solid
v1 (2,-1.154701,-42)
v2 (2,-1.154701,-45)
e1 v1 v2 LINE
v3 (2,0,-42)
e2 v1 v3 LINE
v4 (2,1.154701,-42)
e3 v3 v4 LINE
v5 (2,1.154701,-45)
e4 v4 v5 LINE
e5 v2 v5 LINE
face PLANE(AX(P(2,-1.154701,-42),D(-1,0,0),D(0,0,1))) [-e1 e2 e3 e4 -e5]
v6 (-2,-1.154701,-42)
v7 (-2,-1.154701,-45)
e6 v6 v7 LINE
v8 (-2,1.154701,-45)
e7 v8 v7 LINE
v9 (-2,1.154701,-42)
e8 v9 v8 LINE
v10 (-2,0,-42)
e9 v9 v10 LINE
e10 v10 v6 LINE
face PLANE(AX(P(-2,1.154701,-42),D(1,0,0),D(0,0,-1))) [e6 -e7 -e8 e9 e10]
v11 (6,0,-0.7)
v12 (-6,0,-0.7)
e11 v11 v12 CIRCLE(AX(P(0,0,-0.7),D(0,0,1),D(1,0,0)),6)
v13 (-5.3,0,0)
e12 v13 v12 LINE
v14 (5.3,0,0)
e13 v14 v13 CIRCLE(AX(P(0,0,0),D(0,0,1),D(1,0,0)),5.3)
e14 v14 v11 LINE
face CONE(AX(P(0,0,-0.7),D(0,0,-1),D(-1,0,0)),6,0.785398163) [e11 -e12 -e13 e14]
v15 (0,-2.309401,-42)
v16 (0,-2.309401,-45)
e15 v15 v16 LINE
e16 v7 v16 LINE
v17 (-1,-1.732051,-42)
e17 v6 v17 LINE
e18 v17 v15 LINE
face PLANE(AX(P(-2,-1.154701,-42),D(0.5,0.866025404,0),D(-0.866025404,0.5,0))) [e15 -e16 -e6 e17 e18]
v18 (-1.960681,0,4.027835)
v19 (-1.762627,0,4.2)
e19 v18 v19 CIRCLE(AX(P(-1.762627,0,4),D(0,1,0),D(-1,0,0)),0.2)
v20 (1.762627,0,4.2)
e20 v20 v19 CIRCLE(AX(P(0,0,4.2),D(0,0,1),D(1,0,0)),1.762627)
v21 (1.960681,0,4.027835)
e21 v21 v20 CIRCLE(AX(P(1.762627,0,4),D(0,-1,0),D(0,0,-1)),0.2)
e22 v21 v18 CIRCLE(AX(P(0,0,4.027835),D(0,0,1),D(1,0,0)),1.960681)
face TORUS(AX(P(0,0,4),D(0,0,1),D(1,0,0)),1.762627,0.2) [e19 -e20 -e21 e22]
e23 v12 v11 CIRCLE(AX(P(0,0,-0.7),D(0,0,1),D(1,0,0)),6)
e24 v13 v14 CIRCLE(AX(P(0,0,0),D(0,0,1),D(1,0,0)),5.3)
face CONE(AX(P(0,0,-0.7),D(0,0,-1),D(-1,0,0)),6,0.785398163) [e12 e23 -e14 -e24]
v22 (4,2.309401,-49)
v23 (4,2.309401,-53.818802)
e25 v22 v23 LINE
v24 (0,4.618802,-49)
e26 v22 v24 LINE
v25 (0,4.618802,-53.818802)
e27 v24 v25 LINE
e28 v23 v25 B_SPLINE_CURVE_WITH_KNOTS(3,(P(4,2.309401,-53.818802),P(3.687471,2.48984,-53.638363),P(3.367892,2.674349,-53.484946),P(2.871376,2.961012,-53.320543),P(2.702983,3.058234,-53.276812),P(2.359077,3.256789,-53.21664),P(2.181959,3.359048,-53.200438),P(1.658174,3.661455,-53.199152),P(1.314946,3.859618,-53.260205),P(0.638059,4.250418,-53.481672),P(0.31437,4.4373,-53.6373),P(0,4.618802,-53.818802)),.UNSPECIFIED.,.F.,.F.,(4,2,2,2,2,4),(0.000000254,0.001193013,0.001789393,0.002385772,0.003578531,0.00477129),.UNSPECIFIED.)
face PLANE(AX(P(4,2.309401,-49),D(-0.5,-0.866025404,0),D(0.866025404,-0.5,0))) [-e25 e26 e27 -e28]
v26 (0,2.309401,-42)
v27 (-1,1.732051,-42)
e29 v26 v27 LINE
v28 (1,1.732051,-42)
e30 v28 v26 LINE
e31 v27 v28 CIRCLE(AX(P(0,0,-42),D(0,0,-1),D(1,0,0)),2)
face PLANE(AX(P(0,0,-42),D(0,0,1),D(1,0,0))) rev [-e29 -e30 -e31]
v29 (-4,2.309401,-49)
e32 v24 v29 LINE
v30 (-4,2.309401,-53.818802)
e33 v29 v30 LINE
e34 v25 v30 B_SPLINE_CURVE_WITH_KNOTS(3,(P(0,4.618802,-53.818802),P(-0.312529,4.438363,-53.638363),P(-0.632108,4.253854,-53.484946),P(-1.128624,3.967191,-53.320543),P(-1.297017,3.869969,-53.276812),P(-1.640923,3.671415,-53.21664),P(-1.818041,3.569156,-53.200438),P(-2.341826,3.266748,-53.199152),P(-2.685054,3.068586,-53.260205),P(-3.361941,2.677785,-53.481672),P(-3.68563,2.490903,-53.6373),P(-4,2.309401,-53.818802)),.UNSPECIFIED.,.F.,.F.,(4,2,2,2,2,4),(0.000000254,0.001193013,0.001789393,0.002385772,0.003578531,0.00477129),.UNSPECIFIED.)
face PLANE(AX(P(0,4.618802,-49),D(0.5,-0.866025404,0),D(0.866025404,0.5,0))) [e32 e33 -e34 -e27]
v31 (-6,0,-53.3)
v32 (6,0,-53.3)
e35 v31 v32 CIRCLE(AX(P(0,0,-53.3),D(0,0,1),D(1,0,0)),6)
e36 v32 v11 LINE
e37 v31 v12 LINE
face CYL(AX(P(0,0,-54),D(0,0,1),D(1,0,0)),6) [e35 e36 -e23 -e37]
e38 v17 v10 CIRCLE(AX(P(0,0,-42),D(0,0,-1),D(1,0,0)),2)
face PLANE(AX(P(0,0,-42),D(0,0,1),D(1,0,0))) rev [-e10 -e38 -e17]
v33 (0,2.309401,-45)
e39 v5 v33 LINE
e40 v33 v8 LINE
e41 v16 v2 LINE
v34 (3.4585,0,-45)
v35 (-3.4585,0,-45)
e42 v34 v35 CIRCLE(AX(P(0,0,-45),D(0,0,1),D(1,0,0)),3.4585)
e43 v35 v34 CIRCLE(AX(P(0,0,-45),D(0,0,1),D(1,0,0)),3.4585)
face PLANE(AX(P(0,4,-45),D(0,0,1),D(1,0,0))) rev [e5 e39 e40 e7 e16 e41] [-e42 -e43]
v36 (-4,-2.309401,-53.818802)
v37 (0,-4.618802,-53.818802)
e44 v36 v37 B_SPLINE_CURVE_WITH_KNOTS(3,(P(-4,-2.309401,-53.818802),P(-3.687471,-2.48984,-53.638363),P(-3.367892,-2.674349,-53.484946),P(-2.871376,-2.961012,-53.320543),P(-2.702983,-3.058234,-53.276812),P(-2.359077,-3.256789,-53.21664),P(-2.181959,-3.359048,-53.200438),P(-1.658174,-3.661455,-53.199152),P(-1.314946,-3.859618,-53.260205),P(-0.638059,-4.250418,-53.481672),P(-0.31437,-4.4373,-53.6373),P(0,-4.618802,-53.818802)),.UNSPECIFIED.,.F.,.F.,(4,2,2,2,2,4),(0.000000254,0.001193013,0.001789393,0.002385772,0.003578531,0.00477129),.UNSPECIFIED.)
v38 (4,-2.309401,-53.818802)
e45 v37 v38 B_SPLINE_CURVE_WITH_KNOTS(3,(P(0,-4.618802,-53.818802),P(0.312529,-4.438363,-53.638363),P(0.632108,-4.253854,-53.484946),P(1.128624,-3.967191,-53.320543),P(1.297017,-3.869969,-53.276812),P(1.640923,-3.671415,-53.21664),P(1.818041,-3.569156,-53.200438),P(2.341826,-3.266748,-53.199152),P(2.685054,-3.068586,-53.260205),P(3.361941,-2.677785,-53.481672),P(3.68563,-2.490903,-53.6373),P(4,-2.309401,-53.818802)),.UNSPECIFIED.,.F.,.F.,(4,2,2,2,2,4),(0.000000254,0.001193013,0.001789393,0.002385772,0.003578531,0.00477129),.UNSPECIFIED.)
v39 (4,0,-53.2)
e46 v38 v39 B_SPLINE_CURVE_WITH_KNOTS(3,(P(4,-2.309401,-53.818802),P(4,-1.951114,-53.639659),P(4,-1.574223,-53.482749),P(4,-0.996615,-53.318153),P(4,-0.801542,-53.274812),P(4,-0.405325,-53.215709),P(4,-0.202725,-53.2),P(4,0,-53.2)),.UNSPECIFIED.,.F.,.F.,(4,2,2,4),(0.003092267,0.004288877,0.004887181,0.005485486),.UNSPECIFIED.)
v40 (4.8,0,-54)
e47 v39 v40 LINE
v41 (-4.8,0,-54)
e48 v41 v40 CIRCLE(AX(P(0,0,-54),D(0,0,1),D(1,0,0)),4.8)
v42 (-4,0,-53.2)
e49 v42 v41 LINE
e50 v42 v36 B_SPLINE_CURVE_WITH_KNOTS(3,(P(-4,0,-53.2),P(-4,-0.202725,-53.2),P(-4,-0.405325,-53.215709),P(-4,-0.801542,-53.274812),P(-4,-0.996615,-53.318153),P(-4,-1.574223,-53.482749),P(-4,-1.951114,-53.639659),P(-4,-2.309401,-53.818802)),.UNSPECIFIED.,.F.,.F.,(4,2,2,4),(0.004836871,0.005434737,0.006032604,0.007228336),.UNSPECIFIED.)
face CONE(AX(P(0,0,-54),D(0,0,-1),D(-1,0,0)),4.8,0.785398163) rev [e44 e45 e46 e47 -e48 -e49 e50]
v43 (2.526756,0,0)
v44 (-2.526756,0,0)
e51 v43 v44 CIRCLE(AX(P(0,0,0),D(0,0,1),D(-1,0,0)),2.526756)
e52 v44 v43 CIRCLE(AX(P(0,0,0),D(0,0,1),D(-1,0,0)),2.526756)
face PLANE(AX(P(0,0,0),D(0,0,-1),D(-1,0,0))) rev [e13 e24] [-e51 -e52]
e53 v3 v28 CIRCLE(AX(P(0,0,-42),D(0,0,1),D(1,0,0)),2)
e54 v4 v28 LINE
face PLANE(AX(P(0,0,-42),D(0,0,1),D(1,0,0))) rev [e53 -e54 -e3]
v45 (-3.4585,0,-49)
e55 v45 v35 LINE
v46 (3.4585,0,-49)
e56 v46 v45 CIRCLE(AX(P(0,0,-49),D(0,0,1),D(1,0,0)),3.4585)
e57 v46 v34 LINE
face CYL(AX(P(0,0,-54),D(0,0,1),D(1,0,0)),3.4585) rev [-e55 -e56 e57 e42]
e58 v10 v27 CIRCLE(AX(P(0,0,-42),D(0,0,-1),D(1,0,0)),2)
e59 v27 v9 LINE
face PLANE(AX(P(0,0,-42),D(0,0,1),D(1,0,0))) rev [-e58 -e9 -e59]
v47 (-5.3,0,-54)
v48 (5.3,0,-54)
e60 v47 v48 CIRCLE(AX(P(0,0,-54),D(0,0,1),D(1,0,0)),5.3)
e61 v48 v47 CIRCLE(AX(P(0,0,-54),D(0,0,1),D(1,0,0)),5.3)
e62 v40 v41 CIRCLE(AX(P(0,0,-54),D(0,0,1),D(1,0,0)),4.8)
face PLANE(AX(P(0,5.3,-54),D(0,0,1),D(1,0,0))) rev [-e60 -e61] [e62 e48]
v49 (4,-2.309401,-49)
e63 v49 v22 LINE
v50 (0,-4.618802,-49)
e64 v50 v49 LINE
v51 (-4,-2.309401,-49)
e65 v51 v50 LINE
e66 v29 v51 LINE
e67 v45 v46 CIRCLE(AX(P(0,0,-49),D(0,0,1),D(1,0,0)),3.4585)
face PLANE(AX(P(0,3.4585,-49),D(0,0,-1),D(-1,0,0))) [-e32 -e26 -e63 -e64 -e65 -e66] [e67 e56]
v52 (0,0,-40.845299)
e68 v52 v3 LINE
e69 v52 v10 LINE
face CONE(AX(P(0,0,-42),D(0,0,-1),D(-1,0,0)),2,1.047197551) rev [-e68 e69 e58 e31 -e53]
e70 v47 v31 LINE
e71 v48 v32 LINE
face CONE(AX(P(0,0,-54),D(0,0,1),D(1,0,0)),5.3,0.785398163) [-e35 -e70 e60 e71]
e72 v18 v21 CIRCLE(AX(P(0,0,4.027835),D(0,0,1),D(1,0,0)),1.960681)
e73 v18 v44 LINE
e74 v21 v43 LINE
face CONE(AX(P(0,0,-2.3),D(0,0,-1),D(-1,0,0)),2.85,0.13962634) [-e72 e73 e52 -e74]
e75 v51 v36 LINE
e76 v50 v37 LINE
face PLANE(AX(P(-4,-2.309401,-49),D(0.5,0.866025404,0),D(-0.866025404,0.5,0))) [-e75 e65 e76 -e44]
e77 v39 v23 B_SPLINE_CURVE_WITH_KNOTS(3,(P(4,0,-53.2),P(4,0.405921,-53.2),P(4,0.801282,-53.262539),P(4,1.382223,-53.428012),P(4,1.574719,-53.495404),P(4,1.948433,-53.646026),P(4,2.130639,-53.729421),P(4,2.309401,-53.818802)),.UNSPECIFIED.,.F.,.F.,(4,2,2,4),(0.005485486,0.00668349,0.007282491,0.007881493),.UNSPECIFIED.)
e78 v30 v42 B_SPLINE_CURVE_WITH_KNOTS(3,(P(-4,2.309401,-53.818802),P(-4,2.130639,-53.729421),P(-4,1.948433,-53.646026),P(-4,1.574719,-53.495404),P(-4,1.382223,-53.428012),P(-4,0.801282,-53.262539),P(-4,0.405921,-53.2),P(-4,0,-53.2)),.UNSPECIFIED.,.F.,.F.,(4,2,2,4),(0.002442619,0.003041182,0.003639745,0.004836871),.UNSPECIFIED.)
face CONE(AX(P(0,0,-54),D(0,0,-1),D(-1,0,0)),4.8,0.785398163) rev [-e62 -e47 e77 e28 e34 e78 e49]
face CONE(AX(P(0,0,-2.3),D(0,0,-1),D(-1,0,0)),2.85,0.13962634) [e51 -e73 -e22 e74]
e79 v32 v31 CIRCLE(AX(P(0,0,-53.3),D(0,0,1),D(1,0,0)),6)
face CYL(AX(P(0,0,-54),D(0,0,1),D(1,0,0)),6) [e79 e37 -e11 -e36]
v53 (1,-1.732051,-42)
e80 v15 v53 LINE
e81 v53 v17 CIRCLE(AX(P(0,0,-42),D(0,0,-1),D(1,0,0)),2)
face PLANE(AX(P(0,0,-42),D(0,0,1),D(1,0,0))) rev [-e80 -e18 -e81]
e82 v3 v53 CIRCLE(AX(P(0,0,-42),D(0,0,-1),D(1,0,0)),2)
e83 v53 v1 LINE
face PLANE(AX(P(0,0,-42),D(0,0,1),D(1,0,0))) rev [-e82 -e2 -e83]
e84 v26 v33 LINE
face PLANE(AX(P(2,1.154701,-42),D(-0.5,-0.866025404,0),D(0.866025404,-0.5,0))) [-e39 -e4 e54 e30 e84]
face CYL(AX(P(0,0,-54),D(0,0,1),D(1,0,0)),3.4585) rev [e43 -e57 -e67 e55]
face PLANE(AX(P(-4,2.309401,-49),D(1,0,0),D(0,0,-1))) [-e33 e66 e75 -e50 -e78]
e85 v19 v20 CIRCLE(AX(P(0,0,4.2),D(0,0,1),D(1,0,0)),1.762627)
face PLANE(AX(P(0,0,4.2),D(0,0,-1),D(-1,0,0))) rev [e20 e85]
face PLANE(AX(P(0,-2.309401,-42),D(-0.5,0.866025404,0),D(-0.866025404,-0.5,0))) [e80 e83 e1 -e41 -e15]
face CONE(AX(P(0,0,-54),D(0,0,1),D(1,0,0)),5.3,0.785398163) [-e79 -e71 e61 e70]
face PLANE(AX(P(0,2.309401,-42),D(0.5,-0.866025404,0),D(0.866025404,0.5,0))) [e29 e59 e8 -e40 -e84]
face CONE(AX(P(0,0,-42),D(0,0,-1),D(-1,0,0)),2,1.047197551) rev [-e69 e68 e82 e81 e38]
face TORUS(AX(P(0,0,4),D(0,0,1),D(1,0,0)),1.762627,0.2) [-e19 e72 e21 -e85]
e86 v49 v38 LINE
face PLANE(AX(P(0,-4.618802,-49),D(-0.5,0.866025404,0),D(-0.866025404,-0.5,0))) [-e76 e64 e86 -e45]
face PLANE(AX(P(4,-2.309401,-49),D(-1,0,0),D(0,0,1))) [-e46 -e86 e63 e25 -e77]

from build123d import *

# Parameters (mm, degrees)
CUT_EXTRUDE1_DEPTH = 5
SKETCH5_W          = 12
SKETCH5_H          = 4
CUT_EXTRUDE2_DEPTH = 3


with BuildPart() as part:
    # Sketch1 → Revolve1 (revolve)
    with BuildSketch(Plane(origin=(0, 0, 0), x_dir=(0, 0, -1), z_dir=(1, 0, 0)), mode=Mode.PRIVATE) as revolve1_sk:
        Polygon((0, 0), (0, 5.3), (0.7, 6), (53.3, 6), (54, 5.3), (54, 0), align=None)
    revolve(revolve1_sk.sketch.rotate(Axis((0, 0, -54), (0, 0, 1)), 270), axis=Axis((0, 0, -54), (0, 0, 1)))

    # Sketch2 → Cut-Revolve1 (revolve, cut)
    with BuildSketch(Plane(origin=(0, 0, 0), x_dir=(0, 0, -1), z_dir=(1, 0, 0)), mode=Mode.PRIVATE) as cut_revolve1_sk:
        Polygon((37, 0), (37, 3.4585), (49, 3.4585), (49, 4), (53.2, 4), (54, 4.8), (54, 0), align=None)
    revolve(cut_revolve1_sk.sketch.rotate(Axis((0, 0, -54), (0, 0, 1)), 270), axis=Axis((0, 0, -54), (0, 0, 1)), mode=Mode.SUBTRACT)

    # Sketch3 → Revolve2 (revolve)
    with BuildSketch(Plane(origin=(0, 0, 0), x_dir=(0, 0, -1), z_dir=(1, 0, 0)), mode=Mode.PRIVATE) as revolve2_sk:
        with BuildLine():
            Line((-4.2, 0), (-4.2, 1.762627227))
            ThreePointArc((-4.2, 1.762627227), (-4.150941916, 1.893839033), (-4.02783462, 1.960680841))
            Line((-4.02783462, 1.960680841), (2.3, 2.85))
            Line((2.3, 2.85), (2.3, 0))
            Line((2.3, 0), (-4.2, 0))
        make_face()
    revolve(revolve2_sk.sketch.rotate(Axis((0, 0, -2.3), (0, 0, 1)), 90), axis=Axis((0, 0, -2.3), (0, 0, 1)))

    # Sketch4 → Cut-Extrude1 (cut)
    with BuildSketch(Plane.XY.offset(-54)):
        Polygon((-4, -2.309401077), (0, -4.618802154), (4, -2.309401077), (4, 2.309401077), (0, 4.618802154), (-4, 2.309401077), align=None)
    extrude(amount=CUT_EXTRUDE1_DEPTH, mode=Mode.SUBTRACT)

    # Sketch5 → Revolve3 (revolve)
    with BuildSketch(Plane(origin=(0, 0, 0), x_dir=(0, 0, -1), z_dir=(1, 0, 0)), mode=Mode.PRIVATE) as revolve3_sk:
        with Locations((39, 2)):
            Rectangle(SKETCH5_W, SKETCH5_H)
    revolve(revolve3_sk.sketch.rotate(Axis((0, 0, -45), (0, 0, 1)), 270), axis=Axis((0, 0, -45), (0, 0, 1)))

    # Sketch6 → Cut-Extrude2 (cut)
    with BuildSketch(Plane.XY.offset(-45)):
        Polygon((-2, -1.154700538), (0, -2.309401077), (2, -1.154700538), (2, 1.154700538), (0, 2.309401077), (-2, 1.154700538), align=None)
    extrude(amount=CUT_EXTRUDE2_DEPTH, mode=Mode.SUBTRACT)

    # Sketch7 → Cut-Revolve2 (revolve, cut)
    with BuildSketch(Plane(origin=(0, 0, 0), x_dir=(0, 0, -1), z_dir=(1, 0, 0)), mode=Mode.PRIVATE) as cut_revolve2_sk:
        Polygon((40.845299462, 0), (42, 2), (42, 0), align=None)
    revolve(cut_revolve2_sk.sketch.rotate(Axis((0, 0, -42), (0, 0, 1)), 120.000000088), axis=Axis((0, 0, -42), (0, 0, 1)), mode=Mode.SUBTRACT)


solid = part.part
